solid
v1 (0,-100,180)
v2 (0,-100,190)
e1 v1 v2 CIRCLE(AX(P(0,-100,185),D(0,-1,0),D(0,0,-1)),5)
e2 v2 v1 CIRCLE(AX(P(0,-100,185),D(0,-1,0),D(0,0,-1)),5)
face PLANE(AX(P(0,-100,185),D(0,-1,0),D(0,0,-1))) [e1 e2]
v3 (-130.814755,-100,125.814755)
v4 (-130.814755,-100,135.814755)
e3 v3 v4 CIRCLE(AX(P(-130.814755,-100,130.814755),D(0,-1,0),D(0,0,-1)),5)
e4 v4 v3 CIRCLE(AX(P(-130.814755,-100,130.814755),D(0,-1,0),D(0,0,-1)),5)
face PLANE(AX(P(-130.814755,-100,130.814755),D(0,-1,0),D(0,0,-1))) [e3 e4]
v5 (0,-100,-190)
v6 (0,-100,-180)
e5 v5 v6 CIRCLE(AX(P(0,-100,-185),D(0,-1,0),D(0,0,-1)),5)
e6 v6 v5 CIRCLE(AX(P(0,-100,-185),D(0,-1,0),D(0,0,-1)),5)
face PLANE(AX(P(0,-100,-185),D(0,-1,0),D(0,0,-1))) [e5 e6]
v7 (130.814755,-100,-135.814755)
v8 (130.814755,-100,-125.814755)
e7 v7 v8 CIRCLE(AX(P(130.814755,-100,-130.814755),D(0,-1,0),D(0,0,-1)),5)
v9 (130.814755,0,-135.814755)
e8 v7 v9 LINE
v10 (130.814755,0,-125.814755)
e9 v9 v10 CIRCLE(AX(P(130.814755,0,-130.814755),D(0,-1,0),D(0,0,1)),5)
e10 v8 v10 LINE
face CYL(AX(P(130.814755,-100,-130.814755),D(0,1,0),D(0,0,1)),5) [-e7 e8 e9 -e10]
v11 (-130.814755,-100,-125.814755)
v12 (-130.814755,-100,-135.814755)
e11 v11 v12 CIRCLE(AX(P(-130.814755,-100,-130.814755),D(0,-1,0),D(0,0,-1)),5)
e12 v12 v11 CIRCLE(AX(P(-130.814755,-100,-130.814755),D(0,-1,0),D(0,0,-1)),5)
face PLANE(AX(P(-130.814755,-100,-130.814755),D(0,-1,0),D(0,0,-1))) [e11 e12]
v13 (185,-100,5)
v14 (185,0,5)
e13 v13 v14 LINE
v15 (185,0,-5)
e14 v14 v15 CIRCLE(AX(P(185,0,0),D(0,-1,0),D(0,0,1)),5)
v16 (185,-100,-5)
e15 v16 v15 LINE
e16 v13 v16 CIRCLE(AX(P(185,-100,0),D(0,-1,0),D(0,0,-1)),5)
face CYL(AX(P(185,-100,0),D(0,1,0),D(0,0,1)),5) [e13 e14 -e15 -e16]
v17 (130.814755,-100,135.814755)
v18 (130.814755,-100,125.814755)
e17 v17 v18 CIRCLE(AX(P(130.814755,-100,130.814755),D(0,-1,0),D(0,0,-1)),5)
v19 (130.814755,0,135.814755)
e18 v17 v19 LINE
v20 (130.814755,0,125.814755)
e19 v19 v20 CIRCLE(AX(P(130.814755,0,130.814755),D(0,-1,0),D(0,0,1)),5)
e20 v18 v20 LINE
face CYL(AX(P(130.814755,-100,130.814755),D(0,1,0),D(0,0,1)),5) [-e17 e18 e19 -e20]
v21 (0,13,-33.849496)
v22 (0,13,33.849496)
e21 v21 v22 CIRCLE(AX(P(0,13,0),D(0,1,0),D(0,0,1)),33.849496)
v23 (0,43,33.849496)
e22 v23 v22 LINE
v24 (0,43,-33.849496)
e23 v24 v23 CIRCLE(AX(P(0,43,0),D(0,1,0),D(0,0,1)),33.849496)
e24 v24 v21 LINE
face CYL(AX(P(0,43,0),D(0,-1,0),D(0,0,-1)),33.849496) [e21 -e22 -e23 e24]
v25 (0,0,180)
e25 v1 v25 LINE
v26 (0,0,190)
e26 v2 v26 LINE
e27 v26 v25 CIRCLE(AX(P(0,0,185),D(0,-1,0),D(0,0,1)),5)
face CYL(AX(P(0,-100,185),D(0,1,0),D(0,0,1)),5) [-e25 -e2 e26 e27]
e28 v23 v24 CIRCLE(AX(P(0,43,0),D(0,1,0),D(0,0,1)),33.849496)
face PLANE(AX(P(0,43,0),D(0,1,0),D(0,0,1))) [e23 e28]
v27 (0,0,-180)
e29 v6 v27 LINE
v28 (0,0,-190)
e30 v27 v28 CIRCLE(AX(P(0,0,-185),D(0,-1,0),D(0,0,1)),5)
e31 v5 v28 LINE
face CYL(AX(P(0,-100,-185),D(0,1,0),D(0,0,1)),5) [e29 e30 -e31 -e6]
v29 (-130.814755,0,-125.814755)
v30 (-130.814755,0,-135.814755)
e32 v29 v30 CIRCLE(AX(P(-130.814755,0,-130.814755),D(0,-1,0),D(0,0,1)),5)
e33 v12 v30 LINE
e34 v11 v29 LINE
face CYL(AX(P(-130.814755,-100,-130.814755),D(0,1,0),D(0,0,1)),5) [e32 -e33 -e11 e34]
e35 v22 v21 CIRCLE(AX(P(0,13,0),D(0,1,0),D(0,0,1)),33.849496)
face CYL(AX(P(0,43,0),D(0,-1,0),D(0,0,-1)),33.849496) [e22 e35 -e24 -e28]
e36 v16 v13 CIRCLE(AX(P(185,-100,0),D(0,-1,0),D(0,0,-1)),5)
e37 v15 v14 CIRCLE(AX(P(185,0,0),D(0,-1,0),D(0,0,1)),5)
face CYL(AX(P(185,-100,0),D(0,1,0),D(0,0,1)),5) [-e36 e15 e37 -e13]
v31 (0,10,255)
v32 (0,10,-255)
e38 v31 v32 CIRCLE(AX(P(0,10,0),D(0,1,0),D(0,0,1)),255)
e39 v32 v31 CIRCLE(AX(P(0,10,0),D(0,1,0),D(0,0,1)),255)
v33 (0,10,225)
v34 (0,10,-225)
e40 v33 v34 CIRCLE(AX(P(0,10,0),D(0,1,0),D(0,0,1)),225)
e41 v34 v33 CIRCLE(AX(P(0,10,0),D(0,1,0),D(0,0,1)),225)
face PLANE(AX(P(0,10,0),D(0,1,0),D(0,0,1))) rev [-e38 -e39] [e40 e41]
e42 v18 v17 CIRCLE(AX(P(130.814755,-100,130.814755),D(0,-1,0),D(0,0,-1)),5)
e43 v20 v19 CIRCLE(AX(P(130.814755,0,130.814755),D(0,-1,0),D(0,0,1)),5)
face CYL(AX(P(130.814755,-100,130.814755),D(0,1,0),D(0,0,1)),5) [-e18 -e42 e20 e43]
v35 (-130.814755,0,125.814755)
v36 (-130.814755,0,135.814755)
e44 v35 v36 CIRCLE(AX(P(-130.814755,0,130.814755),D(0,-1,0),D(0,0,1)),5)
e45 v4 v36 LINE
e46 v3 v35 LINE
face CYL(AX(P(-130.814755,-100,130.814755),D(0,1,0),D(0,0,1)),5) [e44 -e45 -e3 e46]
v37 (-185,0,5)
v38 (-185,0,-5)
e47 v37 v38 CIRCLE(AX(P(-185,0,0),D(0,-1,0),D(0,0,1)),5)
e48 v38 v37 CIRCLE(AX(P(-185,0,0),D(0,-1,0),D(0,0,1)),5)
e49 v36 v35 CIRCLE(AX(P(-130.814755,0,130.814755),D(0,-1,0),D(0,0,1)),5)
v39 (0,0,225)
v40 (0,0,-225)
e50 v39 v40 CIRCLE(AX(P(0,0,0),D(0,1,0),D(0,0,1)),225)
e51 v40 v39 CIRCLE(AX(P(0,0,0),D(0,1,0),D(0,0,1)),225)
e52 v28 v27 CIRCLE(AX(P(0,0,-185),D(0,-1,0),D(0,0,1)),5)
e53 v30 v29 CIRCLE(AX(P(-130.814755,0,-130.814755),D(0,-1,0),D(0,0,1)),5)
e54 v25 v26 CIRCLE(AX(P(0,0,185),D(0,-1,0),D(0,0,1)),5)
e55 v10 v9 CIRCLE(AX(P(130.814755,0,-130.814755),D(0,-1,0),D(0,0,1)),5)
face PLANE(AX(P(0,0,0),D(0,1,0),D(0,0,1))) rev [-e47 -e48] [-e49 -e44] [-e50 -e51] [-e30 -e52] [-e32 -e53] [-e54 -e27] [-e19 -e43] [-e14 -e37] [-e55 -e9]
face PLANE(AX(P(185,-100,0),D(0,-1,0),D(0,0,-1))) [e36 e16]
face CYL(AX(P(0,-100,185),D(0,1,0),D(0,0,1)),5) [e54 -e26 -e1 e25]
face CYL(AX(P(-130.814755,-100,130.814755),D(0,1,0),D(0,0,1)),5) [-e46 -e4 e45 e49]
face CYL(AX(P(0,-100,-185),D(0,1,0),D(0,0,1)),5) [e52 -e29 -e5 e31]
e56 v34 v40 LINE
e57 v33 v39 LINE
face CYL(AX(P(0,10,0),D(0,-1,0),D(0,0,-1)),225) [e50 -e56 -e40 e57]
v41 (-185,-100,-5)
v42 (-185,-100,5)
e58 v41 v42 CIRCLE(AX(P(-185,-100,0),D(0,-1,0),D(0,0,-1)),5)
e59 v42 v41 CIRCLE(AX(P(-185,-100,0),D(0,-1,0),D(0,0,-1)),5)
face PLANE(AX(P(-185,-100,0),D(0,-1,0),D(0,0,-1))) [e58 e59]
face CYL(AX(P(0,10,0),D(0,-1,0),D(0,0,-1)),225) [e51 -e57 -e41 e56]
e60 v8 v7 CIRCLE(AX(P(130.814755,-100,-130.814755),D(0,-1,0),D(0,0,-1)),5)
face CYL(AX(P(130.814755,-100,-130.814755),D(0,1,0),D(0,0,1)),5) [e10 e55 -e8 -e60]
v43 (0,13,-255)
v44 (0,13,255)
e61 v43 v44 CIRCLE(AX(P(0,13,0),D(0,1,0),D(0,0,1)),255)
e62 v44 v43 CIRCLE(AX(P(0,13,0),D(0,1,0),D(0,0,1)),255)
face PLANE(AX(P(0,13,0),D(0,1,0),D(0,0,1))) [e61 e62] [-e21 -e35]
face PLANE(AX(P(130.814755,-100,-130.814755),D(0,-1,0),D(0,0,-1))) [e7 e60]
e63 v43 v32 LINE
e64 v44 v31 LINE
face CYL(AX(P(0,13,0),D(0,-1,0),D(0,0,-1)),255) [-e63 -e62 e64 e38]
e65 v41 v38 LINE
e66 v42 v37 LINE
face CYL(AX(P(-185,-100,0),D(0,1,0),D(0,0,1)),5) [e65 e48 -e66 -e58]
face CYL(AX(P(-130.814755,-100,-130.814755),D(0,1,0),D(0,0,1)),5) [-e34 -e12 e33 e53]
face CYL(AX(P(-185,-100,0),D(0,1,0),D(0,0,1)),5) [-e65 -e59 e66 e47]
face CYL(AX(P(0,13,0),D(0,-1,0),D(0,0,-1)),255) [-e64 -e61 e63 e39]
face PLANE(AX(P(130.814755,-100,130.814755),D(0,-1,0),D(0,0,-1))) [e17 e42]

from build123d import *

# Parameters (mm, degrees)
SKETCH1_R           = 225
BOSS_EXTRUDE2_DEPTH = 10
SKETCH2_R           = 5
BOSS_EXTRUDE3_DEPTH = 100
SKETCH3_R           = 255
BOSS_EXTRUDE5_DEPTH = 3
SKETCH7_R           = 33.849496271
BOSS_EXTRUDE6_DEPTH = 30


with BuildPart() as part:
    # Sketch1 → Boss-Extrude2 (new body)
    with BuildSketch(Plane(origin=(0, 0, 0), x_dir=(1, 0, 0), z_dir=(0, 1, 0))):
        with Locations(Location((0, 0, 0), (0, 0, 270))):
            Circle(SKETCH1_R)
    extrude(amount=BOSS_EXTRUDE2_DEPTH)

    # Sketch2 → Boss-Extrude3 (add)
    with BuildSketch(Plane.XZ):
        with Locations(Location((-185, 0, 0), (0, 0, 90))):
            Circle(SKETCH2_R)
        with Locations(Location((-130.81475452, 130.81475452, 0), (0, 0, 90))):
            Circle(SKETCH2_R)
        with Locations(Location((0, 185, 0), (0, 0, 90))):
            Circle(SKETCH2_R)
        with Locations(Location((130.81475452, 130.81475452, 0), (0, 0, 90))):
            Circle(SKETCH2_R)
        with Locations(Location((185, 0, 0), (0, 0, 90))):
            Circle(SKETCH2_R)
        with Locations(Location((130.81475452, -130.81475452, 0), (0, 0, 90))):
            Circle(SKETCH2_R)
        with Locations(Location((0, -185, 0), (0, 0, 90))):
            Circle(SKETCH2_R)
        with Locations(Location((-130.81475452, -130.81475452, 0), (0, 0, 90))):
            Circle(SKETCH2_R)
    extrude(amount=BOSS_EXTRUDE3_DEPTH)

    # Sketch3 → Boss-Extrude5 (add)
    with BuildSketch(Plane(origin=(0, 10, 0), x_dir=(1, 0, 0), z_dir=(0, 1, 0))):
        with Locations(Location((0, 0, 0), (0, 0, 270))):
            Circle(SKETCH3_R)
    extrude(amount=BOSS_EXTRUDE5_DEPTH)

    # Sketch7 → Boss-Extrude6 (add)
    with BuildSketch(Plane(origin=(0, 13, 0), x_dir=(1, 0, 0), z_dir=(0, 1, 0))):
        with Locations(Location((0, 0, 0), (0, 0, 270))):
            Circle(SKETCH7_R)
    extrude(amount=BOSS_EXTRUDE6_DEPTH)


solid = part.part
